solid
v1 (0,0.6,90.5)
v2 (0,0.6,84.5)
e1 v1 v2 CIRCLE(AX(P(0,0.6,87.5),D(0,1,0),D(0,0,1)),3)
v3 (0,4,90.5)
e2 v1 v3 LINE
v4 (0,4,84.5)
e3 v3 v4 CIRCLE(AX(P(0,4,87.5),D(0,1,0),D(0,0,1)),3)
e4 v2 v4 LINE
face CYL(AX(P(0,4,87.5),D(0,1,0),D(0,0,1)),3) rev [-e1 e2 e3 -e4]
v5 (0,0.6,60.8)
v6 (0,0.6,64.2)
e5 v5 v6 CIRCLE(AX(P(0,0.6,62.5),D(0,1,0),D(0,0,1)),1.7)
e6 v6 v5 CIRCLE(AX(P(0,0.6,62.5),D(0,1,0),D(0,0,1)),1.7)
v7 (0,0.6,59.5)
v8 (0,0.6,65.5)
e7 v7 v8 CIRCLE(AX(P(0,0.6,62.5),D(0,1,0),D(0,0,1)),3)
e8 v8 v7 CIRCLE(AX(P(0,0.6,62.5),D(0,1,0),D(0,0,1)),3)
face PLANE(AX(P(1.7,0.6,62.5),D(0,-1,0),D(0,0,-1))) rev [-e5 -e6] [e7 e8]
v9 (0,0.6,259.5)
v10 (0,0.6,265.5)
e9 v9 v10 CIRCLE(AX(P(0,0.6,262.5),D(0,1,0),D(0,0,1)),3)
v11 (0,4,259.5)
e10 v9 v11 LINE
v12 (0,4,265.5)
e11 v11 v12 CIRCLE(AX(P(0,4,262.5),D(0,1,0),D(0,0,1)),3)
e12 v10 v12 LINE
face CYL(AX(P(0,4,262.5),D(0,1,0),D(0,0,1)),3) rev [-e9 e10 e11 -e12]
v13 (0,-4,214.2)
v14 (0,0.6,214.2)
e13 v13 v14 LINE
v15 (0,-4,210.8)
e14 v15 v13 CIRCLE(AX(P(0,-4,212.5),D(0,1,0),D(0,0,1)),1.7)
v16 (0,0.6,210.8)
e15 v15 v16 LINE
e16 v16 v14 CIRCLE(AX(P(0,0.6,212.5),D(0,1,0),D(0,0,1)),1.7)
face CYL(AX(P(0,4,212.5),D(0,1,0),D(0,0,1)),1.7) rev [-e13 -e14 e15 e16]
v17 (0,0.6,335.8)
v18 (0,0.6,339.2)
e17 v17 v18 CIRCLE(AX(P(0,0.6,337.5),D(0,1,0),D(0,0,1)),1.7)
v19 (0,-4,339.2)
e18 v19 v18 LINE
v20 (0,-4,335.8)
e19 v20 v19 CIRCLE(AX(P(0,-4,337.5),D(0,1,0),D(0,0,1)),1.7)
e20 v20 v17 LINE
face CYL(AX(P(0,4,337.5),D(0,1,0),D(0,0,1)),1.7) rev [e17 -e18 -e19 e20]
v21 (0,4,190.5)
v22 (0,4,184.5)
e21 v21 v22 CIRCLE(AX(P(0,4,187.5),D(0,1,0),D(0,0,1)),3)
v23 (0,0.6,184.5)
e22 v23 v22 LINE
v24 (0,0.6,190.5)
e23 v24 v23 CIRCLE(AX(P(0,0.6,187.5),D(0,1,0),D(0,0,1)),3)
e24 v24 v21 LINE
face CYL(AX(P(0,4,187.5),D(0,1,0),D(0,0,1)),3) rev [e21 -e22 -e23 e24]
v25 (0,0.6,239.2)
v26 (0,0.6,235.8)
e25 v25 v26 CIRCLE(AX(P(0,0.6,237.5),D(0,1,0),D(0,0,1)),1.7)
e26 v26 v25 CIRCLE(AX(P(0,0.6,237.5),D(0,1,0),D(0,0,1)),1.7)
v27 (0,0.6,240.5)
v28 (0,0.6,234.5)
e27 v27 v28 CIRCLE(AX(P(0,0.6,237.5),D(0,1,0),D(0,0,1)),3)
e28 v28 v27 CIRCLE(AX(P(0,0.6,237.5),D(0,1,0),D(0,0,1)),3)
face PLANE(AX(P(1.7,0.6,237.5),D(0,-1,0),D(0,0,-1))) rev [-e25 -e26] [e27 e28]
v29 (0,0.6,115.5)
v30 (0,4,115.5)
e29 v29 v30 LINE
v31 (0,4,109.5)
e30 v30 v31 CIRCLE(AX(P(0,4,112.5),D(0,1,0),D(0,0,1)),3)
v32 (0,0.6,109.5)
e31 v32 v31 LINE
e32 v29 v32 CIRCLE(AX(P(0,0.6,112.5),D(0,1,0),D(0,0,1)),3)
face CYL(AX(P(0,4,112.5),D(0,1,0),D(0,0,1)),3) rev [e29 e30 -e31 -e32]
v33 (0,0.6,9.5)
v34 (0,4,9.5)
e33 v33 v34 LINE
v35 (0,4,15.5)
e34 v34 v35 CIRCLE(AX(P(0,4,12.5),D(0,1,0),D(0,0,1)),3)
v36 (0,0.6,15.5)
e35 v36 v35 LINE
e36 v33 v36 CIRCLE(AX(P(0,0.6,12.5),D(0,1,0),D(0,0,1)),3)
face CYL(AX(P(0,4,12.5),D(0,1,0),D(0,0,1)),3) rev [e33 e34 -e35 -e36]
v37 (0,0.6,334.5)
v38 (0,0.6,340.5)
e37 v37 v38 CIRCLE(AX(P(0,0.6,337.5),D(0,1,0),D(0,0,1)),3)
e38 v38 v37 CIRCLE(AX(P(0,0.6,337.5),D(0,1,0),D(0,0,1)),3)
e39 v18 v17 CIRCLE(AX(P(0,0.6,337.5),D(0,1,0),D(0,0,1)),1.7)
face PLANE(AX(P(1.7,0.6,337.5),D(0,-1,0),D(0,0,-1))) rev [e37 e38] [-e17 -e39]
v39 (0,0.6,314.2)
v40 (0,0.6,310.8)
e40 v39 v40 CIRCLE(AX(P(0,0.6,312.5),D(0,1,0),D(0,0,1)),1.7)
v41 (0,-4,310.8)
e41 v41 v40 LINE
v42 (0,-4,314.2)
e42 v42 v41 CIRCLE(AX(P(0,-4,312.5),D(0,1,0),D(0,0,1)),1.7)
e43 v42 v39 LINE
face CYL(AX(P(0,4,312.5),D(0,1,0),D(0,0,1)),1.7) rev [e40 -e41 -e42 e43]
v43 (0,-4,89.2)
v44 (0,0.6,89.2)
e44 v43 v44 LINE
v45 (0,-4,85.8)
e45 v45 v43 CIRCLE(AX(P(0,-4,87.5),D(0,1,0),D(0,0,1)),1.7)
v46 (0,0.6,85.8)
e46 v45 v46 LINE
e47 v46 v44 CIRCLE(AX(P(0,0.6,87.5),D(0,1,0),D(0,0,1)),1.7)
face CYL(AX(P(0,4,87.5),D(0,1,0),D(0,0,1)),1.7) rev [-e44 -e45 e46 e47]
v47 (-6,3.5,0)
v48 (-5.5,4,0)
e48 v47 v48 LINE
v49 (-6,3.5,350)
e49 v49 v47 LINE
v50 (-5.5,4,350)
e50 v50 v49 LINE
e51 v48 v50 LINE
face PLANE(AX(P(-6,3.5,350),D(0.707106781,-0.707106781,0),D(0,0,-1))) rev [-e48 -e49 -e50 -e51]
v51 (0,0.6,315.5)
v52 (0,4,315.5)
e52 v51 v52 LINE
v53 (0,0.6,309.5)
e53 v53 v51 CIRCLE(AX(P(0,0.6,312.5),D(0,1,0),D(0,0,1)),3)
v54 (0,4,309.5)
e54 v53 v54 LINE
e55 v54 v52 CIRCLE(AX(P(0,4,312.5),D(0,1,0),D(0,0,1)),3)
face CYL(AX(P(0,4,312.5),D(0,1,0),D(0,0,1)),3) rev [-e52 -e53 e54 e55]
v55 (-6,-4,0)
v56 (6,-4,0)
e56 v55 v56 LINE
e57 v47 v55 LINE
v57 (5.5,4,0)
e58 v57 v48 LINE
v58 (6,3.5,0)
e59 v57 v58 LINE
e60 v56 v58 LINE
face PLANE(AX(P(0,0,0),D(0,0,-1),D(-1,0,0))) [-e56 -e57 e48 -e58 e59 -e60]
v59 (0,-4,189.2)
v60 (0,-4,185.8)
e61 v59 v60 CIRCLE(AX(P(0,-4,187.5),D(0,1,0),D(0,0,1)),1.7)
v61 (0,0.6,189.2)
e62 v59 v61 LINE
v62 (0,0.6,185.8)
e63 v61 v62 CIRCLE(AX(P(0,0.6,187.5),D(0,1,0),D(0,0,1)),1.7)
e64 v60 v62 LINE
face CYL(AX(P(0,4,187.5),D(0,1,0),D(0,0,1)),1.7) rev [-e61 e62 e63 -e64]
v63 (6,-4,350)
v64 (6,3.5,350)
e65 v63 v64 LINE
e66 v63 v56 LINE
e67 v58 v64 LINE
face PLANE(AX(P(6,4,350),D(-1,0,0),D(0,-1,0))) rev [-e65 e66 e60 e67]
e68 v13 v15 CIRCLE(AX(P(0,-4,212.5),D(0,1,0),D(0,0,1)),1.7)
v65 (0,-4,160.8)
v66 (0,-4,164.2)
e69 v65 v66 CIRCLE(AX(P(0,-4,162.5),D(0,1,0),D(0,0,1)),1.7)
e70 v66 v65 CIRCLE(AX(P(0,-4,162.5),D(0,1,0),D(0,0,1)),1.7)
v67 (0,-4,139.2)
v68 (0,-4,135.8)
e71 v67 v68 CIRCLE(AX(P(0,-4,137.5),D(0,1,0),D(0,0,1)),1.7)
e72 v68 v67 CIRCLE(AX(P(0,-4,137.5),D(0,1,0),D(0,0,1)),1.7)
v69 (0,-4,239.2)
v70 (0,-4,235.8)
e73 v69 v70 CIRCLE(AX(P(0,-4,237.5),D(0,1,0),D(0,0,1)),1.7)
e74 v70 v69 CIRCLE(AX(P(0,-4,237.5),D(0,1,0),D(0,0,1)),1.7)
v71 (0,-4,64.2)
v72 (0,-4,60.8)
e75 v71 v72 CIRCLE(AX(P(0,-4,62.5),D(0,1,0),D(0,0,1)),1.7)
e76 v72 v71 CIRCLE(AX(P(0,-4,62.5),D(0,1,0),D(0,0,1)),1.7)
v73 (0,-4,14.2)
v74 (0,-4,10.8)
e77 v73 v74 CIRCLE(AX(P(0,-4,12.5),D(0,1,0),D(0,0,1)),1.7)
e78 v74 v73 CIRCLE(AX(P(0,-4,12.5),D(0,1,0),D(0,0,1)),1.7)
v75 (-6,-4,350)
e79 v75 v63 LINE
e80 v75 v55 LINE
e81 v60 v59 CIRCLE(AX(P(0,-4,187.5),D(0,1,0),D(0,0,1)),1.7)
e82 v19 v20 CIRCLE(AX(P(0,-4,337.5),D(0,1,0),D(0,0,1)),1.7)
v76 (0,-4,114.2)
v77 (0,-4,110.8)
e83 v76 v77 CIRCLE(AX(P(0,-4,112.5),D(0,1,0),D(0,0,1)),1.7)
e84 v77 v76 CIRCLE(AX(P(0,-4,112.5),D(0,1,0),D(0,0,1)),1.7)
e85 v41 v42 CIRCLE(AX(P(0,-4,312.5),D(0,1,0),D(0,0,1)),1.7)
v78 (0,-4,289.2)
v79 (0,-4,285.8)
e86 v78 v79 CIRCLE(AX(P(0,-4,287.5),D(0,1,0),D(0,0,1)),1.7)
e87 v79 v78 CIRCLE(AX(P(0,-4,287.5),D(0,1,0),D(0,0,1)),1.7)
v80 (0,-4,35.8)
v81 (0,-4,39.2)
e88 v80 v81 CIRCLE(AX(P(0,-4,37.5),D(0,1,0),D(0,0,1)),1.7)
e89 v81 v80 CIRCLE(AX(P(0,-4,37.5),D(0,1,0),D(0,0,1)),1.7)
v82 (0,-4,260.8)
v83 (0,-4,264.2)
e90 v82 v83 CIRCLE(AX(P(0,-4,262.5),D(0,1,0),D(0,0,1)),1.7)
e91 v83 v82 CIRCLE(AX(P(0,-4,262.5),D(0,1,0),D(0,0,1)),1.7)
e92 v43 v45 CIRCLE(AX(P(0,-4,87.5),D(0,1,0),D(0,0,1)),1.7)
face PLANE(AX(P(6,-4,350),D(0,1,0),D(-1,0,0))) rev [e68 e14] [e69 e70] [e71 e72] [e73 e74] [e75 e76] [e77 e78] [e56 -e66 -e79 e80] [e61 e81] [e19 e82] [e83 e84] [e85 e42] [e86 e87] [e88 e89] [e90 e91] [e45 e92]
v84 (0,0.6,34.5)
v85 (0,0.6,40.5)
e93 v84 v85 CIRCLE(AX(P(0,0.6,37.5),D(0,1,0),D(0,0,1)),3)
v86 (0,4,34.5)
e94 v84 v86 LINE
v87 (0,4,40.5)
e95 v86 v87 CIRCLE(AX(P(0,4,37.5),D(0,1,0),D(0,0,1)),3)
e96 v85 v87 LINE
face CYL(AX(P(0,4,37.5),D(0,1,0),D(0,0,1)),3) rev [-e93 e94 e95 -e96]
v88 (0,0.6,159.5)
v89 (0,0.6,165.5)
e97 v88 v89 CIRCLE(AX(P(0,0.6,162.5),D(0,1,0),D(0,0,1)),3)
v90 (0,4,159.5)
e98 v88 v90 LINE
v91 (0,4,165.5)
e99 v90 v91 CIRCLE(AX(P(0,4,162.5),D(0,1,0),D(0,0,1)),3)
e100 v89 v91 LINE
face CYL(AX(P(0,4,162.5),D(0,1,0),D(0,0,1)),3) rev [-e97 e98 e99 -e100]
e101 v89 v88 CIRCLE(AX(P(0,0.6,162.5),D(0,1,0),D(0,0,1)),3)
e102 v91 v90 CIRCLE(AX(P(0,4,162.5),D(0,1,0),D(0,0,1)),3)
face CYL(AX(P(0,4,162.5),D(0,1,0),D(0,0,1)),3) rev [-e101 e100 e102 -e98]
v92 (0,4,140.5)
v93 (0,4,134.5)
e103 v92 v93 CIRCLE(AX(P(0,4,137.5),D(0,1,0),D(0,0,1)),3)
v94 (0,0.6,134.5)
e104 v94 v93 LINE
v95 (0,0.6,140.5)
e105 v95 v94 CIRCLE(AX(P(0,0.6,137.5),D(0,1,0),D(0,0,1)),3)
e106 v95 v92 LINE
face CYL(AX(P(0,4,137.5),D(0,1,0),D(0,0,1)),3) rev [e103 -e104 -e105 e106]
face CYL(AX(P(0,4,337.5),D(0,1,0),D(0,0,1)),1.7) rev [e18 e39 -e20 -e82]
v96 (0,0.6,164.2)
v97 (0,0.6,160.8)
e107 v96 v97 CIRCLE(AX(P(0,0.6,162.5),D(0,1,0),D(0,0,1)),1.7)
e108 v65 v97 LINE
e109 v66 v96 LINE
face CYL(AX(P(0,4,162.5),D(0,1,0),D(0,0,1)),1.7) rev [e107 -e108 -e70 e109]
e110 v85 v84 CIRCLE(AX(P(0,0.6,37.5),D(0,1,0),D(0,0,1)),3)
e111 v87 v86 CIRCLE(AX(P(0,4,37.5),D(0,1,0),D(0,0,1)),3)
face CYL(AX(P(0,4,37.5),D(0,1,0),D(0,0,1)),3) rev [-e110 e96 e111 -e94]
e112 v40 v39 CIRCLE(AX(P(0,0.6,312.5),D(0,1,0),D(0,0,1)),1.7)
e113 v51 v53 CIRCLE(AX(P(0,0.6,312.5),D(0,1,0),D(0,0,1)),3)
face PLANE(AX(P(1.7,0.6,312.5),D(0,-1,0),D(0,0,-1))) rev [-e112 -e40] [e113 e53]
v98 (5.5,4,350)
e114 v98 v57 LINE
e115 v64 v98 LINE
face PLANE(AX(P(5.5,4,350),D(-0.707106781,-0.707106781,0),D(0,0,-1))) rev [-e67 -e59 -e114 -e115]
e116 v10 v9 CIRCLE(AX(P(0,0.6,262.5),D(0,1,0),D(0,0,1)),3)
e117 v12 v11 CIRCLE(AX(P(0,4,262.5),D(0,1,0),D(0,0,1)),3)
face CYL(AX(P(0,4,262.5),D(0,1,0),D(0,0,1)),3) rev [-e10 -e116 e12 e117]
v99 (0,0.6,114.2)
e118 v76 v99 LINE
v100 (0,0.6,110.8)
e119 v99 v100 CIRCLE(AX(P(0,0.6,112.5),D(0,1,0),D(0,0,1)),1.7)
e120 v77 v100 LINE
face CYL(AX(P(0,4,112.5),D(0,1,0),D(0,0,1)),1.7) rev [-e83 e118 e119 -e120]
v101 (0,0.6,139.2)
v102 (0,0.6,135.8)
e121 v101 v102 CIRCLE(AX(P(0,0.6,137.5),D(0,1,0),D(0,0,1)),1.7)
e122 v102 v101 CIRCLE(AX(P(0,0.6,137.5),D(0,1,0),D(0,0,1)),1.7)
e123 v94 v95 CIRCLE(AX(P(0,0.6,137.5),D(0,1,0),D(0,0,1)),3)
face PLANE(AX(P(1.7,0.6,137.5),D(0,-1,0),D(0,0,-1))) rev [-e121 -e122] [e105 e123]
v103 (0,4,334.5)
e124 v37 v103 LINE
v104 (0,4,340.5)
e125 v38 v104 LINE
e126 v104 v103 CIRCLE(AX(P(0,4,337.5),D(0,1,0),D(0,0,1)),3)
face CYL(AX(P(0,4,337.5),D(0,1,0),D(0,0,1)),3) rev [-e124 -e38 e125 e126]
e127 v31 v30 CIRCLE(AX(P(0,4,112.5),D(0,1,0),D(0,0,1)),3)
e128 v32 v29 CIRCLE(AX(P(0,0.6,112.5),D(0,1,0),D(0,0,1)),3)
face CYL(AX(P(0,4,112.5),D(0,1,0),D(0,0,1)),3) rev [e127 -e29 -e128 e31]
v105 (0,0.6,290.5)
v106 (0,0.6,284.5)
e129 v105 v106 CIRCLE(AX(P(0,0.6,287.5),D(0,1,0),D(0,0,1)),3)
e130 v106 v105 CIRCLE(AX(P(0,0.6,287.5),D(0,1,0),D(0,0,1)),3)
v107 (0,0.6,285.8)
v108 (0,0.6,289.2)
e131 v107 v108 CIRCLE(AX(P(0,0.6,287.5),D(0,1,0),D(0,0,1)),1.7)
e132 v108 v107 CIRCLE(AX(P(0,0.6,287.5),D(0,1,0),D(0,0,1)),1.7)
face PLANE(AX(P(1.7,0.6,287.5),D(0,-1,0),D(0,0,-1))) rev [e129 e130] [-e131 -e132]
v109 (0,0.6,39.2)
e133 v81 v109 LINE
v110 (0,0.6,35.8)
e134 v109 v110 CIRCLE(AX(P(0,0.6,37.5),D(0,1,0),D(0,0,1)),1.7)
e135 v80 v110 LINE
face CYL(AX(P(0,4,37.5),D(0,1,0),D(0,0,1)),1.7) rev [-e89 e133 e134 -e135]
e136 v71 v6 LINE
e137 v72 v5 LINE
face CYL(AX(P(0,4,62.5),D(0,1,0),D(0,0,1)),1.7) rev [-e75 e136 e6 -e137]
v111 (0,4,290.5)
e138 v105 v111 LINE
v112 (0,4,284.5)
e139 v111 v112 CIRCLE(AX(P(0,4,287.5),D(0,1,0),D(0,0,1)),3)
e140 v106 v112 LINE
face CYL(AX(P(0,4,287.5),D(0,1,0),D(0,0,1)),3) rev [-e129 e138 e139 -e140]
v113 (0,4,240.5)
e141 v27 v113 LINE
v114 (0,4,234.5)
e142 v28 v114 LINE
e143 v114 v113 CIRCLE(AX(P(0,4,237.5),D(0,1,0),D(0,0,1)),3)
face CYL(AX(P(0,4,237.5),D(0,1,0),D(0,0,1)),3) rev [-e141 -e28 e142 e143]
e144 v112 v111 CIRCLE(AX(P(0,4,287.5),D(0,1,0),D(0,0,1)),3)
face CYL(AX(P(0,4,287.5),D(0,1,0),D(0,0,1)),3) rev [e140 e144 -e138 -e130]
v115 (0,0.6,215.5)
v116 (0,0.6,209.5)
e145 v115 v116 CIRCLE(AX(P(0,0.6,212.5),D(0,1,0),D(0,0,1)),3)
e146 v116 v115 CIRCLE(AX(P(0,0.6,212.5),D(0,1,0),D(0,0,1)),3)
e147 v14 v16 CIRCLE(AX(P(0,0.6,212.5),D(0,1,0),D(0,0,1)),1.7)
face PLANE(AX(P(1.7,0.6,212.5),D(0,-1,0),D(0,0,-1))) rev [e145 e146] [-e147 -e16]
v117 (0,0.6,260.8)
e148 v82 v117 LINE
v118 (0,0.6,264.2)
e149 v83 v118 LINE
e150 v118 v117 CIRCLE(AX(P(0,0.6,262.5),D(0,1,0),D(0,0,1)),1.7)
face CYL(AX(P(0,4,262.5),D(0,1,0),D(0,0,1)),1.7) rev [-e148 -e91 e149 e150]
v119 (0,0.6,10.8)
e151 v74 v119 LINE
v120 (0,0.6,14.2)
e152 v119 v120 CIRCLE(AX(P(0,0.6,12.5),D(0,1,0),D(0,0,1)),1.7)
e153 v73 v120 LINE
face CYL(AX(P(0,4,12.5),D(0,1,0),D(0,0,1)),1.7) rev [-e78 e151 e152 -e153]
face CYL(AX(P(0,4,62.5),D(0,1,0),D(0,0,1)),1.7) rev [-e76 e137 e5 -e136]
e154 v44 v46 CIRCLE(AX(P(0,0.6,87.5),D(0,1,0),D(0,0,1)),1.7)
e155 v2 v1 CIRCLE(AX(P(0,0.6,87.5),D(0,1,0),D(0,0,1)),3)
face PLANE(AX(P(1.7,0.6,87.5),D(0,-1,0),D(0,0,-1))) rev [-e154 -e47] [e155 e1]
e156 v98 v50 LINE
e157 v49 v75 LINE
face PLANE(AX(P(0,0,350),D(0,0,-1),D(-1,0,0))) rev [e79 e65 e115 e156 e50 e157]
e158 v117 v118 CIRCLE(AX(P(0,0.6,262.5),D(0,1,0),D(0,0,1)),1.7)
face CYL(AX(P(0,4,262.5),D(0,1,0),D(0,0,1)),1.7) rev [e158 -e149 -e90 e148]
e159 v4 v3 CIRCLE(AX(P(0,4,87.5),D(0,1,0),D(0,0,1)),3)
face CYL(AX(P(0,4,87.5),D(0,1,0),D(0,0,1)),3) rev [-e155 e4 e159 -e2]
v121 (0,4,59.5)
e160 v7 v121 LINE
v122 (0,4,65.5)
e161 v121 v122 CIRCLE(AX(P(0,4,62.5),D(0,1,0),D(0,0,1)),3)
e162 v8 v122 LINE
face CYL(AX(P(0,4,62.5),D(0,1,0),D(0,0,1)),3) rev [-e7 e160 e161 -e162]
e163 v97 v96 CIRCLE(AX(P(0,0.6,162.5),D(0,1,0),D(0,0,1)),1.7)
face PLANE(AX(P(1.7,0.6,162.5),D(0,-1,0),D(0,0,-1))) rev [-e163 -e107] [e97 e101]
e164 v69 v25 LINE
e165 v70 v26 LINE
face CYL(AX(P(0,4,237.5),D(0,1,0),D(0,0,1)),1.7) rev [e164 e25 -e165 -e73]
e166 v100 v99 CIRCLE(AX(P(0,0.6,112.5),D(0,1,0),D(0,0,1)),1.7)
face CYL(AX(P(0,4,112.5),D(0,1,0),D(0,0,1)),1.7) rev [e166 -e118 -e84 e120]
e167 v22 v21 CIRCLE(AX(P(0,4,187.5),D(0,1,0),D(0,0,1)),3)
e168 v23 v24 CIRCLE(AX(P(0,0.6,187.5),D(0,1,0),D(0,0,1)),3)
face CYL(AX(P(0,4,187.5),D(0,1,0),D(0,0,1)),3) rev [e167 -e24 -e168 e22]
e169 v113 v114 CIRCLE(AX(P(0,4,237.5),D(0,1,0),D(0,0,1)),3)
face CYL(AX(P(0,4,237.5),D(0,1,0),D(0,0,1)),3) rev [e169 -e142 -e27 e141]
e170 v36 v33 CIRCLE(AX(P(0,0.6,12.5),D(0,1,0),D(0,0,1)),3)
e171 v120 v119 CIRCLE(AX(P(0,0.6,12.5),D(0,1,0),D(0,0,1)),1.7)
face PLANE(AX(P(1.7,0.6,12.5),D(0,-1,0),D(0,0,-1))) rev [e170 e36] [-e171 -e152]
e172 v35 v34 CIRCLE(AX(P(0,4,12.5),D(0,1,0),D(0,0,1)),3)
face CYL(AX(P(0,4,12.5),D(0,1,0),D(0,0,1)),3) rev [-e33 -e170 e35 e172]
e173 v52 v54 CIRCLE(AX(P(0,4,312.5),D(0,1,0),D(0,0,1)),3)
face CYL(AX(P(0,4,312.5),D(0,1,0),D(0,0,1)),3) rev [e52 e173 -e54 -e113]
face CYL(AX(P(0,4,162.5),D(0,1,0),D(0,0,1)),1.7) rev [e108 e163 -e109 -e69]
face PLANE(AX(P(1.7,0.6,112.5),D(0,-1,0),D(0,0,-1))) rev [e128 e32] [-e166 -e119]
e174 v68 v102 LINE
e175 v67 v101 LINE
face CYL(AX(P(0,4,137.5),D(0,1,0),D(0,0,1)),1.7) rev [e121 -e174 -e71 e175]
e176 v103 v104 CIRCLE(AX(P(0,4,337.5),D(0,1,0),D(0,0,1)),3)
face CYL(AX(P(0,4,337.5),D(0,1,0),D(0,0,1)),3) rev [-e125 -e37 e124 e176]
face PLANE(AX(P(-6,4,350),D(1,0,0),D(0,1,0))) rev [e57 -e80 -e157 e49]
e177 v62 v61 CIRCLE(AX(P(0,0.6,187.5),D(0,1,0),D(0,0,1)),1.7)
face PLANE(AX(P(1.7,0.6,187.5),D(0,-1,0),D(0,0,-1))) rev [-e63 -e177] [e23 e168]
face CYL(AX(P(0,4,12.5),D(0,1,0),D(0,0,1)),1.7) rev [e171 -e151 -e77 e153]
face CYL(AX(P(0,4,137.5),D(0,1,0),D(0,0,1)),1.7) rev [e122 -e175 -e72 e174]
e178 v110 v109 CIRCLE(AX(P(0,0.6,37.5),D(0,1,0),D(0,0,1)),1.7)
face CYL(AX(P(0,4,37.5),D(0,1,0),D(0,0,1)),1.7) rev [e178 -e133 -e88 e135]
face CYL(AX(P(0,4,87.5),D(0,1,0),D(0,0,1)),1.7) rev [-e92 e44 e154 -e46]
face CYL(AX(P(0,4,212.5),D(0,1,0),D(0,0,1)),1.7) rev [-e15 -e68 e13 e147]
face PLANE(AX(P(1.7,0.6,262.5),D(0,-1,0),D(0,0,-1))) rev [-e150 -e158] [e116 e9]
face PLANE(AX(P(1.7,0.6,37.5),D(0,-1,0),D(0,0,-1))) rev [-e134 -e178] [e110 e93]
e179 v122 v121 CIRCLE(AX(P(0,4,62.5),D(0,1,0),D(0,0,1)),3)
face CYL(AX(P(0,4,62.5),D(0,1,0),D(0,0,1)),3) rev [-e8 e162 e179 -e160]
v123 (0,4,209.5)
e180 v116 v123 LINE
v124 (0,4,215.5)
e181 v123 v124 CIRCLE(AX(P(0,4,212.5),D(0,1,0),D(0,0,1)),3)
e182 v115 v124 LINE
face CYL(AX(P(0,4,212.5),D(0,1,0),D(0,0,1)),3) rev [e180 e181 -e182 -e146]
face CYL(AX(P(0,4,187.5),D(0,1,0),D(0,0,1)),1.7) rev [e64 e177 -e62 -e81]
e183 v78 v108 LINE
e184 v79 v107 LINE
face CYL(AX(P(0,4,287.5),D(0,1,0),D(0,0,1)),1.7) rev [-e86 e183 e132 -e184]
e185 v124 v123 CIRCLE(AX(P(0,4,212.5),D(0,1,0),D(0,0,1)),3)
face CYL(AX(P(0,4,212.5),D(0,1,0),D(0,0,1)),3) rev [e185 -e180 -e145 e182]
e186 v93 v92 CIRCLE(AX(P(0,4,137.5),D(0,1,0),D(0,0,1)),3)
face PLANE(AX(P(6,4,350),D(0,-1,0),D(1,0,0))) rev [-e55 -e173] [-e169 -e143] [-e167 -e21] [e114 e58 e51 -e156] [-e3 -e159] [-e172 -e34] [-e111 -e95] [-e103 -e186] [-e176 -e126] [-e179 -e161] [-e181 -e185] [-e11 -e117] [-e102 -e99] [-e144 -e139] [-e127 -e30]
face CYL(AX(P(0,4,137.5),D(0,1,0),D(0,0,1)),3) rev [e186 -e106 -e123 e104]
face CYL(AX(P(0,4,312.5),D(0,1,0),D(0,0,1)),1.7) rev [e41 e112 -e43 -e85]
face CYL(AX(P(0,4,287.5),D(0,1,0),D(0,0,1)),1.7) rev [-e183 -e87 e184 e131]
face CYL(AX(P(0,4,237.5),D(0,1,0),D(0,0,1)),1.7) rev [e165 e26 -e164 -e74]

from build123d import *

# Parameters (mm, degrees)
SKETCH_1_W                = 12
SKETCH_1_H                = 8
EXTRUDE_1_DEPTH           = 350
CHAMFER_1_SIZE            = 0.5
CHAMFER_2_SIZE            = 0.5
HOLE_WIZARD_1_D           = 3.4
HOLE_WIZARD_1_CBORE_D     = 6
HOLE_WIZARD_1_CBORE_DEPTH = 3.4
PATTERN_LINEAR_1_COUNT    = 14
PATTERN_LINEAR_1_PITCH    = 25


with BuildPart() as part:
    # 草图1 → 凸台-拉伸1 (new body)
    with BuildSketch(Plane.XY):
        Rectangle(SKETCH_1_W, SKETCH_1_H)
    extrude(amount=EXTRUDE_1_DEPTH)

    # 倒角1
    chamfer_1_edges = [part.edges().sort_by_distance(p)[0] for p in [
        (6, 4, 175),
    ]]
    chamfer(chamfer_1_edges, length=CHAMFER_1_SIZE)

    # 倒角2
    chamfer_2_edges = [part.edges().sort_by_distance(p)[0] for p in [
        (-6, 4, 175),
    ]]
    chamfer(chamfer_2_edges, length=CHAMFER_2_SIZE)

    # 打孔尺寸根据内六角圆柱头螺钉的类型1 (through all)
    with Locations(Plane(origin=(0, 4, 0), x_dir=(1, 0, 0), z_dir=(0, 1, 0))):
        with Locations((0, -12.5)):
            hole_wizard_1 = CounterBoreHole(HOLE_WIZARD_1_D / 2, HOLE_WIZARD_1_CBORE_D / 2, HOLE_WIZARD_1_CBORE_DEPTH)

    # 阵列(线性)1: 打孔尺寸根据内六角圆柱头螺钉的类型1 ×14
    with Locations(*[(0, 0, i * PATTERN_LINEAR_1_PITCH) for i in range(1, PATTERN_LINEAR_1_COUNT)]):
        add(hole_wizard_1, mode=Mode.SUBTRACT)


solid = part.part
